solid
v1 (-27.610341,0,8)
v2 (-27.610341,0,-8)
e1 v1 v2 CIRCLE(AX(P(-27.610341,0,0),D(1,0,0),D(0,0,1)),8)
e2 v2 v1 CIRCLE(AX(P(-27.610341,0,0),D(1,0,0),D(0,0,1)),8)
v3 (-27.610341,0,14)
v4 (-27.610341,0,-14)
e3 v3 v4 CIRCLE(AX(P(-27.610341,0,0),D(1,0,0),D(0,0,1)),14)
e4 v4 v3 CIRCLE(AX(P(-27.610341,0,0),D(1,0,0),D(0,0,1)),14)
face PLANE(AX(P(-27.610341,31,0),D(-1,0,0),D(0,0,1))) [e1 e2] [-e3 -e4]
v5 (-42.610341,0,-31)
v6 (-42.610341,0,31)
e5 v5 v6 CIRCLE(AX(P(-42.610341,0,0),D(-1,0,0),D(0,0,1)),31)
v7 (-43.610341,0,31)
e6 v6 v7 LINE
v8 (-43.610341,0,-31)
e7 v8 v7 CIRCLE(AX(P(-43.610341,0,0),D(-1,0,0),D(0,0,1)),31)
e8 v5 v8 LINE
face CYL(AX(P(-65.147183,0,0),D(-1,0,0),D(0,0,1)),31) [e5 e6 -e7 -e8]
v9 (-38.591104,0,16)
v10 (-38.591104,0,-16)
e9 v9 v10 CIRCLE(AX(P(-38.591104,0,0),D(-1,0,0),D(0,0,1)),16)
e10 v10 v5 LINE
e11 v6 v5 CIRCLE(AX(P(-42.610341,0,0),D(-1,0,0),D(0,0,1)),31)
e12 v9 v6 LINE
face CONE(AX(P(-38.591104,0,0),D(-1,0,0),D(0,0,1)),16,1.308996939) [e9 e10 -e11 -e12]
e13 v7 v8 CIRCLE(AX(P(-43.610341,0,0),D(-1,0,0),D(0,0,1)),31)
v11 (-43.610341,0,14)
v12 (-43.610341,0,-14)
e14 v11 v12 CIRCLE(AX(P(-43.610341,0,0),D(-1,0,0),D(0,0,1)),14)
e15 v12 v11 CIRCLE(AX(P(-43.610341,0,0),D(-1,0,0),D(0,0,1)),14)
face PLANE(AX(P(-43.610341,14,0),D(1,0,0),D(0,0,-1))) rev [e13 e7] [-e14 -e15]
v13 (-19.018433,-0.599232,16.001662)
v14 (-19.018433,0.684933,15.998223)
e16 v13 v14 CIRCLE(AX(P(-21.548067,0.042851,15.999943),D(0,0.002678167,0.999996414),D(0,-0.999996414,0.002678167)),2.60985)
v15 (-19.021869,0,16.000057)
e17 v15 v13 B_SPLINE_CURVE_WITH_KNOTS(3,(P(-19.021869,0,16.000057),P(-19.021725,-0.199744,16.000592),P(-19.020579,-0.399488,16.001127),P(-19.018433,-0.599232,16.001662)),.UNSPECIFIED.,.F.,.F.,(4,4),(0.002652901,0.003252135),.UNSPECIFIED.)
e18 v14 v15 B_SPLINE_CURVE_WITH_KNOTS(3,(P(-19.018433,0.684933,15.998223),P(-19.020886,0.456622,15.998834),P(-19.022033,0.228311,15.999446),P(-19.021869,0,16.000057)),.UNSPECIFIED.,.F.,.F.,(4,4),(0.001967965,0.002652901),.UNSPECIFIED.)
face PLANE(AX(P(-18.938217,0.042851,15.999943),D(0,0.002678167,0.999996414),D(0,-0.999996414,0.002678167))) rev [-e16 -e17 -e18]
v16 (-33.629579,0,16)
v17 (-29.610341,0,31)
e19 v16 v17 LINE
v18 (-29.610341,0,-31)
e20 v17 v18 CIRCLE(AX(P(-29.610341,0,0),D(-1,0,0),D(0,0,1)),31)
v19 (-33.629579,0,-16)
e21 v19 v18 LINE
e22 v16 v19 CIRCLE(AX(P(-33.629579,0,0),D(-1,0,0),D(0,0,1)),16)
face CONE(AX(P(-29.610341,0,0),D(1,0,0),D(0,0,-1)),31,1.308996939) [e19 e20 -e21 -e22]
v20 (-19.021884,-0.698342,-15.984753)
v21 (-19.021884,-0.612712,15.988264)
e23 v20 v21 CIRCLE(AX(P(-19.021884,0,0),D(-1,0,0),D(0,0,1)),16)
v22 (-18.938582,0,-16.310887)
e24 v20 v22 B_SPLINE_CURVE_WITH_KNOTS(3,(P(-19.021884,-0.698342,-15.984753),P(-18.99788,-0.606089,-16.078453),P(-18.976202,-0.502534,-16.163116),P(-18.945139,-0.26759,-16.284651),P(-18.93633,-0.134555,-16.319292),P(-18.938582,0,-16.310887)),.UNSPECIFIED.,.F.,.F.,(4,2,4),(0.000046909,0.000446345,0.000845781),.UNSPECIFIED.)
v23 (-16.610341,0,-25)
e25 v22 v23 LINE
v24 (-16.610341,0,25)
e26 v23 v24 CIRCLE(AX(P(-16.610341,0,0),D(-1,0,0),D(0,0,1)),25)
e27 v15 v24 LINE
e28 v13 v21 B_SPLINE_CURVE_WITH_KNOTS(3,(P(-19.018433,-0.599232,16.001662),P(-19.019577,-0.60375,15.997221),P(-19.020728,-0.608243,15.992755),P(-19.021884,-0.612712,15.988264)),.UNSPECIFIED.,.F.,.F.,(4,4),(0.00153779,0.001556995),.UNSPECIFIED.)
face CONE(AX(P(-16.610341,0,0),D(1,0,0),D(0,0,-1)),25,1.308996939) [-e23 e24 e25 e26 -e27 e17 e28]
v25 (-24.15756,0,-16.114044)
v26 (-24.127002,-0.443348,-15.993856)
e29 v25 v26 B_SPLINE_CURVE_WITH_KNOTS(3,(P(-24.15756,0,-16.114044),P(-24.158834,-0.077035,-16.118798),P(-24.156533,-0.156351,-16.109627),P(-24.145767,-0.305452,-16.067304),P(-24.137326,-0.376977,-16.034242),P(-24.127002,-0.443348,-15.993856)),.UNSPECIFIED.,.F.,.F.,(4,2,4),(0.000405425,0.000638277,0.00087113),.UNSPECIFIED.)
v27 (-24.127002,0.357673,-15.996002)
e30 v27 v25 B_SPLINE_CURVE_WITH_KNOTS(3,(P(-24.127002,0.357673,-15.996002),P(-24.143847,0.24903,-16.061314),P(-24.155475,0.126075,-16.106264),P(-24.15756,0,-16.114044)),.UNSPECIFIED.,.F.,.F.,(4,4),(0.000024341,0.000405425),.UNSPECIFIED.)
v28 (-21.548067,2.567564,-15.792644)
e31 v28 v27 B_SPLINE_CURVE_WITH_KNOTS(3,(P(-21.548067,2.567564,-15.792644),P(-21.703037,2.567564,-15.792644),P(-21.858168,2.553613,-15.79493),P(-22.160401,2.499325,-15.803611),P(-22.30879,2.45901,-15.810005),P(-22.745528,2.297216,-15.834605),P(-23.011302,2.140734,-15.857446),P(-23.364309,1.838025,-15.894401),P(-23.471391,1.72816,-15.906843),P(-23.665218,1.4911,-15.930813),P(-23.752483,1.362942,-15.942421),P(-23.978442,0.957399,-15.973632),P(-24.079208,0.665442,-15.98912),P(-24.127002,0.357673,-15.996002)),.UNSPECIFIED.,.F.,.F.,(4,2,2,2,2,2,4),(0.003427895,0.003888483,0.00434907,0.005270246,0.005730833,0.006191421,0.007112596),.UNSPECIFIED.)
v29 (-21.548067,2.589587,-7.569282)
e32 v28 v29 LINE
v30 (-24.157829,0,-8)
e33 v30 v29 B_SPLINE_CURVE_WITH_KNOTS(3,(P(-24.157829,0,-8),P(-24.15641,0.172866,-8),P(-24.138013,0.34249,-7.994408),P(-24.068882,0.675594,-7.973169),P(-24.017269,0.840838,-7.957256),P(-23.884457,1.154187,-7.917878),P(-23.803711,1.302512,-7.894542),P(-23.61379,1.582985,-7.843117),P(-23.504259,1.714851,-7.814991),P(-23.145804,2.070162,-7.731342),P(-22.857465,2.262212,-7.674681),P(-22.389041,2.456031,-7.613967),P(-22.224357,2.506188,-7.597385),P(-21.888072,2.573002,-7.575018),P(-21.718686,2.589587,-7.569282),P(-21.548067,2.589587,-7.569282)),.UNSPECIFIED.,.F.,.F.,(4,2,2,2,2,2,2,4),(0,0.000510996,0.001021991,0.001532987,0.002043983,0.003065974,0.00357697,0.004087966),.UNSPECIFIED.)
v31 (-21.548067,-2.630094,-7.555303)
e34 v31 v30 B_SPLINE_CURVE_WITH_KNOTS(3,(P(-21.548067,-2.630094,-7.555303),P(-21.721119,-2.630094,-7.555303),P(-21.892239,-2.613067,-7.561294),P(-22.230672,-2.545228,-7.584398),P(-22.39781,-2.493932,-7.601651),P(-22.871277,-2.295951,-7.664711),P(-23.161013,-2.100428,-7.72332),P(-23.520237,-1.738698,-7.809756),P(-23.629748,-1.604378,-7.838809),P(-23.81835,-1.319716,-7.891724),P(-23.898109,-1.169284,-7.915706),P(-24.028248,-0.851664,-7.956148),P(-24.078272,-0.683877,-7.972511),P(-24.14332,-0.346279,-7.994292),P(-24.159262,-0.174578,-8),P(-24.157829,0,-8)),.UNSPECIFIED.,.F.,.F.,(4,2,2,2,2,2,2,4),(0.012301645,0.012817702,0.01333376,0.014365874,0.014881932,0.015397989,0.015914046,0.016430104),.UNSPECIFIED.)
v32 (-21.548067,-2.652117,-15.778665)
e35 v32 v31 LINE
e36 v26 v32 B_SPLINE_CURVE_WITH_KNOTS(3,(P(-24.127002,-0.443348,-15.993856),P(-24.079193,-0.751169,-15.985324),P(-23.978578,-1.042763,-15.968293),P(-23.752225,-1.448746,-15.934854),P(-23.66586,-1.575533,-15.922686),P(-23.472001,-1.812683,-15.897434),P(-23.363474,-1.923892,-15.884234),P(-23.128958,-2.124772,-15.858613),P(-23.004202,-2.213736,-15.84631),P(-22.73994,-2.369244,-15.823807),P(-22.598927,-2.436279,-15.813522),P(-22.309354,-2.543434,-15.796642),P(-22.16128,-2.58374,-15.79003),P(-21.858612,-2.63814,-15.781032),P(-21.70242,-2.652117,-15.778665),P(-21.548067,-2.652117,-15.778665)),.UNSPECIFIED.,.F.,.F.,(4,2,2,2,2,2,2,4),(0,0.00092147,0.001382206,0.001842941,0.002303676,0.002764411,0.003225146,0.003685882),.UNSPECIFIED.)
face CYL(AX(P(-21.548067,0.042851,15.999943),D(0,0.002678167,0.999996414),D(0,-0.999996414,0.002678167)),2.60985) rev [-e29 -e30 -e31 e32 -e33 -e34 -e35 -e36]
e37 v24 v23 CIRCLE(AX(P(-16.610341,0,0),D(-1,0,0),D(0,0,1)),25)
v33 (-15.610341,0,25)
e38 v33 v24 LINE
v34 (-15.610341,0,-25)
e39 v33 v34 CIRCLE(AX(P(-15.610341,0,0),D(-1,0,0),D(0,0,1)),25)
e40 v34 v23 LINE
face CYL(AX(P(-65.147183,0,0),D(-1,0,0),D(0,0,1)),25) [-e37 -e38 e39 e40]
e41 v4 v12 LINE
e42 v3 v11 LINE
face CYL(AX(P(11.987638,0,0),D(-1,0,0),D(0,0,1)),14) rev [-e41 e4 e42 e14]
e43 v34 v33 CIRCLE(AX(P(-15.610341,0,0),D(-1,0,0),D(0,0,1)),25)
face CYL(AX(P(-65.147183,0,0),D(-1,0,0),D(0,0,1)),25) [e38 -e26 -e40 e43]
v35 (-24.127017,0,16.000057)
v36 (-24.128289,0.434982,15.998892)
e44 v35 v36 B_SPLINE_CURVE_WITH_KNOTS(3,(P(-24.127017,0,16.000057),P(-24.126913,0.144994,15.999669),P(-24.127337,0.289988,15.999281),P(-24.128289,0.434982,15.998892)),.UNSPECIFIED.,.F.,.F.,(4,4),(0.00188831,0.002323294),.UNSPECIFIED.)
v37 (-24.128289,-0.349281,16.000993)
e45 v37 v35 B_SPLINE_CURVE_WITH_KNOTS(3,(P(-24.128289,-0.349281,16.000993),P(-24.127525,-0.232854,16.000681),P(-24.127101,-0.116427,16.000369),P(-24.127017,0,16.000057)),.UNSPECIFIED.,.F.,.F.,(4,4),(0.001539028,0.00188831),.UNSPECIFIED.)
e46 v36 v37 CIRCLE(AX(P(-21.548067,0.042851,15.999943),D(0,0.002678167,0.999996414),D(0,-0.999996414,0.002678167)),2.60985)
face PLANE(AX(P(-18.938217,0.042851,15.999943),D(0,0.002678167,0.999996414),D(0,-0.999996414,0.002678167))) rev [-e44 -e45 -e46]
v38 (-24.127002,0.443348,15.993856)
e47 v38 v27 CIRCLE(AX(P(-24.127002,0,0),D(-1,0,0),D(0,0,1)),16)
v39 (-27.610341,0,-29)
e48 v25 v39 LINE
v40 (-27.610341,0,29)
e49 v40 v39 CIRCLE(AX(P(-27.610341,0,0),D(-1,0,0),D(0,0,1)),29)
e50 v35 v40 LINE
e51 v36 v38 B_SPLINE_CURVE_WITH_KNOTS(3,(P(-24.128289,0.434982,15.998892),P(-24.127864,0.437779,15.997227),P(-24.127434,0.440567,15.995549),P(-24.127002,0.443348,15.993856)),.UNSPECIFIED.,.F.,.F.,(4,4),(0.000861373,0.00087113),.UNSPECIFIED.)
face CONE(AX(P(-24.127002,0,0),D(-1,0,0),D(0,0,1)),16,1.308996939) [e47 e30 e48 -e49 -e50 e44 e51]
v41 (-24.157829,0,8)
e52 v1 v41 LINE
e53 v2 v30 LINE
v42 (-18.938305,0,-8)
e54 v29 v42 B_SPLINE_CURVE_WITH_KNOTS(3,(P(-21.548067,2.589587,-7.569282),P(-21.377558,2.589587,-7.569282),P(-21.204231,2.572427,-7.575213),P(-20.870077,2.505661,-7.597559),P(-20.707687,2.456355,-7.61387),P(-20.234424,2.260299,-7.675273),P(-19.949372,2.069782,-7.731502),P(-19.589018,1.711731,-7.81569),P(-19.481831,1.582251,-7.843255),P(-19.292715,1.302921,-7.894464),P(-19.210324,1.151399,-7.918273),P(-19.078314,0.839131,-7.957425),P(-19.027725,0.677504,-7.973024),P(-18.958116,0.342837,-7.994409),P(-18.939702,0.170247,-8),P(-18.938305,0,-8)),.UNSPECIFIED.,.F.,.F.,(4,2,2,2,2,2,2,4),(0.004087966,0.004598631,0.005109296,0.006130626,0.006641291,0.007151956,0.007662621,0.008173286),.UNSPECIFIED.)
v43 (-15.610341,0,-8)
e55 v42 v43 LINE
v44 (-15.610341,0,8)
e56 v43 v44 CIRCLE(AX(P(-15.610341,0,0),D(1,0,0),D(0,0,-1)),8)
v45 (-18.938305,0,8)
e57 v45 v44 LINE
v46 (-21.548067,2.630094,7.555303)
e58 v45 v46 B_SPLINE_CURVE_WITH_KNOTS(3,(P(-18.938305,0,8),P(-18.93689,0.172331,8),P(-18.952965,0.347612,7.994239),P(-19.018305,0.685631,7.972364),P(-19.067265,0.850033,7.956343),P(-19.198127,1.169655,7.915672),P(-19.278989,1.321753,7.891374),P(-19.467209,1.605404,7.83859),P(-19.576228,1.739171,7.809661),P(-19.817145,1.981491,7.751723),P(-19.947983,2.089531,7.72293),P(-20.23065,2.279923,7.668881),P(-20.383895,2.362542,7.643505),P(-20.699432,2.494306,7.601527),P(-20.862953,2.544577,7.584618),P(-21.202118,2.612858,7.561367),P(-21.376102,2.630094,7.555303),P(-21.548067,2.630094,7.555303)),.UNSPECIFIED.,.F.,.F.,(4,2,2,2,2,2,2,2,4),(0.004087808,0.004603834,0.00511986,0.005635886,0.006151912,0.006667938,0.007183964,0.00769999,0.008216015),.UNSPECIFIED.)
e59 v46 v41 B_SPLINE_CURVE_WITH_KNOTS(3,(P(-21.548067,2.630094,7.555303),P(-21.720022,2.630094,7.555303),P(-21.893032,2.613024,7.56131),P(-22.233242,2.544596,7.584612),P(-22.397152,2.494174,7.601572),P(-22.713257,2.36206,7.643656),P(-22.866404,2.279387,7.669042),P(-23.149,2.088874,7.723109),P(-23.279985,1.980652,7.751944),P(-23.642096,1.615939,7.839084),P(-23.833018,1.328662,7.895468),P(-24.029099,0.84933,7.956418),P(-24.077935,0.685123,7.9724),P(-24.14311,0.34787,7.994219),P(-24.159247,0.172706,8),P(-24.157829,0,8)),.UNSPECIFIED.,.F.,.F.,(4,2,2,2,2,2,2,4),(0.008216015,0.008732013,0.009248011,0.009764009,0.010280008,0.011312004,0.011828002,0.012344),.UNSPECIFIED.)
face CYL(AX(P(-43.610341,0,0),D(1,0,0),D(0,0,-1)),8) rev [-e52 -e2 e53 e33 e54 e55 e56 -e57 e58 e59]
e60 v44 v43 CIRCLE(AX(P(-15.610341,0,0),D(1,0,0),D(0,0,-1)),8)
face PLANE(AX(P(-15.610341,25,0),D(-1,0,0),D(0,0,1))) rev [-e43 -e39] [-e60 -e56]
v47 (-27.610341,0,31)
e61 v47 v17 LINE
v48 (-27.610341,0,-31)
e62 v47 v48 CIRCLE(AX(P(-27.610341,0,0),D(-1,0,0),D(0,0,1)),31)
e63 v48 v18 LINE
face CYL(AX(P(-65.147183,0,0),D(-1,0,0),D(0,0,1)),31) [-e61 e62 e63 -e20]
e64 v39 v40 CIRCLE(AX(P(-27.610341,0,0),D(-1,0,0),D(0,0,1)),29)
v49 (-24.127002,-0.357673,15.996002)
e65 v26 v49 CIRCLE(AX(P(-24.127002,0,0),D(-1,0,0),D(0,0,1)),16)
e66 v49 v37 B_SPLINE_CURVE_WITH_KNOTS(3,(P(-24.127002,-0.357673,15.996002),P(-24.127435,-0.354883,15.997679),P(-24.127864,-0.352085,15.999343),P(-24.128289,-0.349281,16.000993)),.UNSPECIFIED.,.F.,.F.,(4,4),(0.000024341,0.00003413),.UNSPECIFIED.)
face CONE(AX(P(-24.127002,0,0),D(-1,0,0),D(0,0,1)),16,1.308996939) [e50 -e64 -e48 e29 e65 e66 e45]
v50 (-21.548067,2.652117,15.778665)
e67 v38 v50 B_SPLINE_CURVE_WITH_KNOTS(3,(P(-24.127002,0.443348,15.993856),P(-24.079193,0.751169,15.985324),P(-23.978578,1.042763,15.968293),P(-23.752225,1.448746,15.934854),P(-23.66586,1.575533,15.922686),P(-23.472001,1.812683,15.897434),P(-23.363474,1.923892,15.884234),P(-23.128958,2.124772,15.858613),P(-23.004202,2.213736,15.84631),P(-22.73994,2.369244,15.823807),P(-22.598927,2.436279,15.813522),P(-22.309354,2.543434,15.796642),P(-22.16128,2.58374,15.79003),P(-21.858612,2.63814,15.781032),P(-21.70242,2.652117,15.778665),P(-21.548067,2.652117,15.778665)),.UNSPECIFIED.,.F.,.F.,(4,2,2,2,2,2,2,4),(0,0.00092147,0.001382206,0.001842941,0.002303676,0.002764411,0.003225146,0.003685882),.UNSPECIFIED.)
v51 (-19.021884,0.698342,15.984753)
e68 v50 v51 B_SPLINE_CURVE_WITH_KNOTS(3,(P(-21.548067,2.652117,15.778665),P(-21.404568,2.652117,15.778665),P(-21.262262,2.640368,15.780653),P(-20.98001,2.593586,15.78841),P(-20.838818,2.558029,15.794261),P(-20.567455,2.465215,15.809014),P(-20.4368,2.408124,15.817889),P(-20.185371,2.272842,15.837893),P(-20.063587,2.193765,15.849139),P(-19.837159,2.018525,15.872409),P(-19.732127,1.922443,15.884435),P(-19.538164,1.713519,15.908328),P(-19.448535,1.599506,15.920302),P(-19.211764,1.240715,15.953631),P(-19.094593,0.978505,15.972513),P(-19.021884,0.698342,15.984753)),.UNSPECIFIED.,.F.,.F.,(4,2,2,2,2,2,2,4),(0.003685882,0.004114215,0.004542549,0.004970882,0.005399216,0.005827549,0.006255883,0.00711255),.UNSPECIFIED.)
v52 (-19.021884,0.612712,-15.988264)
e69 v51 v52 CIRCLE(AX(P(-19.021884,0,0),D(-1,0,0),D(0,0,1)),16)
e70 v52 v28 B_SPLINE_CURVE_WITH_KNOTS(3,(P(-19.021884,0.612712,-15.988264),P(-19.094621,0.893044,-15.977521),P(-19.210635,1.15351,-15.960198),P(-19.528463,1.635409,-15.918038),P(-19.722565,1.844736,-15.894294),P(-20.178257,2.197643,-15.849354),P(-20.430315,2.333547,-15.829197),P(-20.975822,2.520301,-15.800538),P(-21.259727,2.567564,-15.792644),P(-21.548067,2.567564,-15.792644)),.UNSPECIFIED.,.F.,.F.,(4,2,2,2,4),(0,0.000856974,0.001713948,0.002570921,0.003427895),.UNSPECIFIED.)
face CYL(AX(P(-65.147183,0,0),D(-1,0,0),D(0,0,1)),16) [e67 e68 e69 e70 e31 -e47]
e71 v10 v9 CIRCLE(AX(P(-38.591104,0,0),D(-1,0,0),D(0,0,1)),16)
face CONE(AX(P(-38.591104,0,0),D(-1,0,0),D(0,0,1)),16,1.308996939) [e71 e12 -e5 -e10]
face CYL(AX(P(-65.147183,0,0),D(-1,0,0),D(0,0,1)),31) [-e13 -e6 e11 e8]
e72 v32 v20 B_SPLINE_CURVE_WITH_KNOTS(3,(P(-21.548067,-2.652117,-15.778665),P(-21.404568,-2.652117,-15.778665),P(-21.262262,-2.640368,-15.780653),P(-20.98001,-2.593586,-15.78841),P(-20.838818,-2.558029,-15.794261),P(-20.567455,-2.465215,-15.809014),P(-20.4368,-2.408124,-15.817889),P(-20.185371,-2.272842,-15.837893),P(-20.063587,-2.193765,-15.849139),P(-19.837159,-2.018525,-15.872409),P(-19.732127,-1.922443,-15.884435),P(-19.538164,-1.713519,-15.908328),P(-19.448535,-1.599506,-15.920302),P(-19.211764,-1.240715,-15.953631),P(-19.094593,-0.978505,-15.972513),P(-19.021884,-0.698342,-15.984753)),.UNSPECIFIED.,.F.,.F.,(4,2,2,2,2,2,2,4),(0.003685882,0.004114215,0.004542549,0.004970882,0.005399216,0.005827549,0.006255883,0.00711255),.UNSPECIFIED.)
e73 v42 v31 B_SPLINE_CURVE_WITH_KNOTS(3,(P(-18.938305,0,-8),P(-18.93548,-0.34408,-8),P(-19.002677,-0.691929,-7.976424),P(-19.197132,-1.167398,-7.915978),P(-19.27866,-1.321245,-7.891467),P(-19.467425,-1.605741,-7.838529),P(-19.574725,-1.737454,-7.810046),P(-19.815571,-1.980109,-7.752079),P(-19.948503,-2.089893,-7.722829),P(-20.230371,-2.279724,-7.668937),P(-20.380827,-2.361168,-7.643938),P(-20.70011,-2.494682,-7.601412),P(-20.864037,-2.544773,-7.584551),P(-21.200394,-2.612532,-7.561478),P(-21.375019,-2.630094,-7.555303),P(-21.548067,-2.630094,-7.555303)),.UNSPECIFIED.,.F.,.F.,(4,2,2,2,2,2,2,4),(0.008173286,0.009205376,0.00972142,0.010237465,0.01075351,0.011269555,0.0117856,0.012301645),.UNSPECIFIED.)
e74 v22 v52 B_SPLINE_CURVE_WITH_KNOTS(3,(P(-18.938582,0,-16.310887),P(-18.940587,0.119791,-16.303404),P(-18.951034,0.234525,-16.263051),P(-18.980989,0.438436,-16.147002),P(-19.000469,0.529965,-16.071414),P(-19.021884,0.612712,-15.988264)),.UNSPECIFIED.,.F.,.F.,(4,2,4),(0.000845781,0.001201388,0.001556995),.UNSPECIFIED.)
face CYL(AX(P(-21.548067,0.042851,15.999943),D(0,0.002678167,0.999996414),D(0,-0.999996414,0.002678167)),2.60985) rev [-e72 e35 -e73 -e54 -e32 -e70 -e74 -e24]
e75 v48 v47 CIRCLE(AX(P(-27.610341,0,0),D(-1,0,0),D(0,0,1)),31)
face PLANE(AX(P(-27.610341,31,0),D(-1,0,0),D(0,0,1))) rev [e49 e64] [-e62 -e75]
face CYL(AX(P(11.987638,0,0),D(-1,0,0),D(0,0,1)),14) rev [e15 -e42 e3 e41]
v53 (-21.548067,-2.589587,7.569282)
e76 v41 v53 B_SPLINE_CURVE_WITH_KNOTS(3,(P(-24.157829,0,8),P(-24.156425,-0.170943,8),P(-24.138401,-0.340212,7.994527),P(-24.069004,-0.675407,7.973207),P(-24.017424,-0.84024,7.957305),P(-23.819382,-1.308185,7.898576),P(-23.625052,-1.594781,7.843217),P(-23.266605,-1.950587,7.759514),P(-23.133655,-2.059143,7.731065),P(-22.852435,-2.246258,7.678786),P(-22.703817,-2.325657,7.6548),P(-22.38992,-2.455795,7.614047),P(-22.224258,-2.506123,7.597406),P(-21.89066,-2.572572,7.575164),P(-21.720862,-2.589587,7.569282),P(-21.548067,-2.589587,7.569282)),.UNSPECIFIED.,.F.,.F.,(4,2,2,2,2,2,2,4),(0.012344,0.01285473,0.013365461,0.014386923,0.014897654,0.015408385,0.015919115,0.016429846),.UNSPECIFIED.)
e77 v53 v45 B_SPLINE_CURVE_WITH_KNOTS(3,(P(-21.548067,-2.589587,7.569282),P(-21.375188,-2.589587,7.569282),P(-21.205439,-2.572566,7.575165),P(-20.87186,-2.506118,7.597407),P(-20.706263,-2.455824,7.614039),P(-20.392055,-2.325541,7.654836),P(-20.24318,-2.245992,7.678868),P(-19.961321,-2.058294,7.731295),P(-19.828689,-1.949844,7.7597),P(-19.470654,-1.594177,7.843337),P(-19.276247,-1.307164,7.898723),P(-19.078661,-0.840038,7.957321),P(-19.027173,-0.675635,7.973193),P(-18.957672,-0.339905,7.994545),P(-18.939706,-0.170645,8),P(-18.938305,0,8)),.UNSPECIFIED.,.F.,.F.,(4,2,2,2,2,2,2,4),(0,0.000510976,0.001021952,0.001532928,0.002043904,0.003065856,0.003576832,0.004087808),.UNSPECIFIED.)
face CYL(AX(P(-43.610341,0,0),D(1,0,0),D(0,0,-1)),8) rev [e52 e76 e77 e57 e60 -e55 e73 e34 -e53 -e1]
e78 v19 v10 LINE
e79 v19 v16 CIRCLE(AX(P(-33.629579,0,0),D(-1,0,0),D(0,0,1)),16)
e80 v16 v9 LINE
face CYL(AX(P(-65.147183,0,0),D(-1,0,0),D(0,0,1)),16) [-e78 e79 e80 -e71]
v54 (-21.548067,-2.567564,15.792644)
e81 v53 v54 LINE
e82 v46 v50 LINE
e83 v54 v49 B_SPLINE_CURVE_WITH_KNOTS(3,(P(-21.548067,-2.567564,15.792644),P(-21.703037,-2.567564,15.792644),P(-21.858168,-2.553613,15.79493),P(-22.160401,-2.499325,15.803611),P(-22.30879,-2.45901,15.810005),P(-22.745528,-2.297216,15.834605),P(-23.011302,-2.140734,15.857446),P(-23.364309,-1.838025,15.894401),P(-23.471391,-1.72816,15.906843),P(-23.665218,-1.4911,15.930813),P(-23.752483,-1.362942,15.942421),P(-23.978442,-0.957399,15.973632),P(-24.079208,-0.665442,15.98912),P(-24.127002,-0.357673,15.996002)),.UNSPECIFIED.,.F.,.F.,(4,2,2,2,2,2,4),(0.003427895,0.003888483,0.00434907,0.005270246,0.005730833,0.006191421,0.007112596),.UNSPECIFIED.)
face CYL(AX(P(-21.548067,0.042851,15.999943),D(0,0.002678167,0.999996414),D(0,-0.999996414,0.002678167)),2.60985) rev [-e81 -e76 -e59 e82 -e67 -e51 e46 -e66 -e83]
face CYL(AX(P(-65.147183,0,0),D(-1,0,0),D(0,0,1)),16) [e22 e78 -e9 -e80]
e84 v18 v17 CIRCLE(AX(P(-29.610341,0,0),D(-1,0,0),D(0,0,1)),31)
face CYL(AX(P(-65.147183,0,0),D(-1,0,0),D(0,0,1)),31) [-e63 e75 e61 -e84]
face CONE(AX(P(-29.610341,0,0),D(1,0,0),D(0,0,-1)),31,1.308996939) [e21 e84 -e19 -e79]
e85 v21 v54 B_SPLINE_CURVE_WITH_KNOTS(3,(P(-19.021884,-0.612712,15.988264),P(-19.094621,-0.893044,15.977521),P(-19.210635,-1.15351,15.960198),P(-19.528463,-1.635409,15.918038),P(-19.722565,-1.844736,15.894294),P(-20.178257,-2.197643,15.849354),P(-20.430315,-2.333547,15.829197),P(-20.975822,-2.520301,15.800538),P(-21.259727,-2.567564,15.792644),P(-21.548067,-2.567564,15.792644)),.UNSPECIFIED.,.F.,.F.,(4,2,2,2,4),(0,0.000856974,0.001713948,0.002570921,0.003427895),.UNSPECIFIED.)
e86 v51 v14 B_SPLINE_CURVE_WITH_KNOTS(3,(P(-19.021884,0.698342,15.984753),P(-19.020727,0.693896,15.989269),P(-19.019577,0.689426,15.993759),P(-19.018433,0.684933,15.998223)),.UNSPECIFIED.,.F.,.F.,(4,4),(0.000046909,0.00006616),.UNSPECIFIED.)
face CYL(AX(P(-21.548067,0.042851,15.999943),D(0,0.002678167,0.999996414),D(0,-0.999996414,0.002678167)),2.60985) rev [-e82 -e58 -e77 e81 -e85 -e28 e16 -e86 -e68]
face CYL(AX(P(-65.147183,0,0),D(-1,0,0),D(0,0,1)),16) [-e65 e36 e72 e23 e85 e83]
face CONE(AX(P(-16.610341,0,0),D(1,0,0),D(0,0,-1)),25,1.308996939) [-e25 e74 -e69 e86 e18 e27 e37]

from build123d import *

# Parameters (mm, degrees)
SKETCH2_R           = 14.854735332
SKETCH2_R_2         = 8
BOSS_EXTRUDE1_DEPTH = 28
SKETCH3_R           = 14
CUT_EXTRUDE1_DEPTH  = 16
SKETCH6_W           = 2.60985
SKETCH6_H           = 47.082912009


with BuildPart() as part:
    # Sketch1 → Revolve1 (revolve)
    with BuildSketch(Plane.XY, mode=Mode.PRIVATE) as revolve1_sk:
        Polygon((-43.610341394, 31), (-42.610341394, 31), (-38.591103508, 16), (-33.62957928, 16), (-29.610341394, 31), (-27.610341394, 31), (-27.610341394, 29), (-24.127001892, 16), (-19.021884126, 16), (-16.610341394, 25), (-15.610341394, 25), (-15.610341394, 14), (-43.610341394, 14), align=None)
    revolve(revolve1_sk.sketch.rotate(Axis((-65.147183499, 0, 0), (1, 0, 0)), 90), axis=Axis((-65.147183499, 0, 0), (1, 0, 0)))

    # Sketch2 → Boss-Extrude1 (add, through all)
    with BuildSketch(Plane(origin=(-15.610341394, 0, 0), x_dir=(0, 0, -1), z_dir=(1, 0, 0))):
        Circle(SKETCH2_R)
        Circle(SKETCH2_R_2, mode=Mode.SUBTRACT)
    extrude(amount=-BOSS_EXTRUDE1_DEPTH)

    # Sketch3 → Cut-Extrude1 (cut)
    with BuildSketch(Plane.ZY.offset(43.610341394)):
        Circle(SKETCH3_R)
    extrude(amount=-CUT_EXTRUDE1_DEPTH, mode=Mode.SUBTRACT)

    # Sketch6 → #5 (0.2055) Diameter Hole1 (revolve, cut)
    with BuildSketch(Plane(origin=(-21.548066642, 0.042850676, 15.999942619), x_dir=(0, -0.9999964137036997, 0.0026781672351362563), z_dir=(1, 0, 0))):
        with Locations((1.304925, 23.541456005)):
            Rectangle(SKETCH6_W, SKETCH6_H)
    revolve(axis=Axis((-21.548066642, 0.059857038, 22.349919846), (0, -0.0026781672351362563, -0.9999964137036995)), mode=Mode.SUBTRACT)


solid = part.part
